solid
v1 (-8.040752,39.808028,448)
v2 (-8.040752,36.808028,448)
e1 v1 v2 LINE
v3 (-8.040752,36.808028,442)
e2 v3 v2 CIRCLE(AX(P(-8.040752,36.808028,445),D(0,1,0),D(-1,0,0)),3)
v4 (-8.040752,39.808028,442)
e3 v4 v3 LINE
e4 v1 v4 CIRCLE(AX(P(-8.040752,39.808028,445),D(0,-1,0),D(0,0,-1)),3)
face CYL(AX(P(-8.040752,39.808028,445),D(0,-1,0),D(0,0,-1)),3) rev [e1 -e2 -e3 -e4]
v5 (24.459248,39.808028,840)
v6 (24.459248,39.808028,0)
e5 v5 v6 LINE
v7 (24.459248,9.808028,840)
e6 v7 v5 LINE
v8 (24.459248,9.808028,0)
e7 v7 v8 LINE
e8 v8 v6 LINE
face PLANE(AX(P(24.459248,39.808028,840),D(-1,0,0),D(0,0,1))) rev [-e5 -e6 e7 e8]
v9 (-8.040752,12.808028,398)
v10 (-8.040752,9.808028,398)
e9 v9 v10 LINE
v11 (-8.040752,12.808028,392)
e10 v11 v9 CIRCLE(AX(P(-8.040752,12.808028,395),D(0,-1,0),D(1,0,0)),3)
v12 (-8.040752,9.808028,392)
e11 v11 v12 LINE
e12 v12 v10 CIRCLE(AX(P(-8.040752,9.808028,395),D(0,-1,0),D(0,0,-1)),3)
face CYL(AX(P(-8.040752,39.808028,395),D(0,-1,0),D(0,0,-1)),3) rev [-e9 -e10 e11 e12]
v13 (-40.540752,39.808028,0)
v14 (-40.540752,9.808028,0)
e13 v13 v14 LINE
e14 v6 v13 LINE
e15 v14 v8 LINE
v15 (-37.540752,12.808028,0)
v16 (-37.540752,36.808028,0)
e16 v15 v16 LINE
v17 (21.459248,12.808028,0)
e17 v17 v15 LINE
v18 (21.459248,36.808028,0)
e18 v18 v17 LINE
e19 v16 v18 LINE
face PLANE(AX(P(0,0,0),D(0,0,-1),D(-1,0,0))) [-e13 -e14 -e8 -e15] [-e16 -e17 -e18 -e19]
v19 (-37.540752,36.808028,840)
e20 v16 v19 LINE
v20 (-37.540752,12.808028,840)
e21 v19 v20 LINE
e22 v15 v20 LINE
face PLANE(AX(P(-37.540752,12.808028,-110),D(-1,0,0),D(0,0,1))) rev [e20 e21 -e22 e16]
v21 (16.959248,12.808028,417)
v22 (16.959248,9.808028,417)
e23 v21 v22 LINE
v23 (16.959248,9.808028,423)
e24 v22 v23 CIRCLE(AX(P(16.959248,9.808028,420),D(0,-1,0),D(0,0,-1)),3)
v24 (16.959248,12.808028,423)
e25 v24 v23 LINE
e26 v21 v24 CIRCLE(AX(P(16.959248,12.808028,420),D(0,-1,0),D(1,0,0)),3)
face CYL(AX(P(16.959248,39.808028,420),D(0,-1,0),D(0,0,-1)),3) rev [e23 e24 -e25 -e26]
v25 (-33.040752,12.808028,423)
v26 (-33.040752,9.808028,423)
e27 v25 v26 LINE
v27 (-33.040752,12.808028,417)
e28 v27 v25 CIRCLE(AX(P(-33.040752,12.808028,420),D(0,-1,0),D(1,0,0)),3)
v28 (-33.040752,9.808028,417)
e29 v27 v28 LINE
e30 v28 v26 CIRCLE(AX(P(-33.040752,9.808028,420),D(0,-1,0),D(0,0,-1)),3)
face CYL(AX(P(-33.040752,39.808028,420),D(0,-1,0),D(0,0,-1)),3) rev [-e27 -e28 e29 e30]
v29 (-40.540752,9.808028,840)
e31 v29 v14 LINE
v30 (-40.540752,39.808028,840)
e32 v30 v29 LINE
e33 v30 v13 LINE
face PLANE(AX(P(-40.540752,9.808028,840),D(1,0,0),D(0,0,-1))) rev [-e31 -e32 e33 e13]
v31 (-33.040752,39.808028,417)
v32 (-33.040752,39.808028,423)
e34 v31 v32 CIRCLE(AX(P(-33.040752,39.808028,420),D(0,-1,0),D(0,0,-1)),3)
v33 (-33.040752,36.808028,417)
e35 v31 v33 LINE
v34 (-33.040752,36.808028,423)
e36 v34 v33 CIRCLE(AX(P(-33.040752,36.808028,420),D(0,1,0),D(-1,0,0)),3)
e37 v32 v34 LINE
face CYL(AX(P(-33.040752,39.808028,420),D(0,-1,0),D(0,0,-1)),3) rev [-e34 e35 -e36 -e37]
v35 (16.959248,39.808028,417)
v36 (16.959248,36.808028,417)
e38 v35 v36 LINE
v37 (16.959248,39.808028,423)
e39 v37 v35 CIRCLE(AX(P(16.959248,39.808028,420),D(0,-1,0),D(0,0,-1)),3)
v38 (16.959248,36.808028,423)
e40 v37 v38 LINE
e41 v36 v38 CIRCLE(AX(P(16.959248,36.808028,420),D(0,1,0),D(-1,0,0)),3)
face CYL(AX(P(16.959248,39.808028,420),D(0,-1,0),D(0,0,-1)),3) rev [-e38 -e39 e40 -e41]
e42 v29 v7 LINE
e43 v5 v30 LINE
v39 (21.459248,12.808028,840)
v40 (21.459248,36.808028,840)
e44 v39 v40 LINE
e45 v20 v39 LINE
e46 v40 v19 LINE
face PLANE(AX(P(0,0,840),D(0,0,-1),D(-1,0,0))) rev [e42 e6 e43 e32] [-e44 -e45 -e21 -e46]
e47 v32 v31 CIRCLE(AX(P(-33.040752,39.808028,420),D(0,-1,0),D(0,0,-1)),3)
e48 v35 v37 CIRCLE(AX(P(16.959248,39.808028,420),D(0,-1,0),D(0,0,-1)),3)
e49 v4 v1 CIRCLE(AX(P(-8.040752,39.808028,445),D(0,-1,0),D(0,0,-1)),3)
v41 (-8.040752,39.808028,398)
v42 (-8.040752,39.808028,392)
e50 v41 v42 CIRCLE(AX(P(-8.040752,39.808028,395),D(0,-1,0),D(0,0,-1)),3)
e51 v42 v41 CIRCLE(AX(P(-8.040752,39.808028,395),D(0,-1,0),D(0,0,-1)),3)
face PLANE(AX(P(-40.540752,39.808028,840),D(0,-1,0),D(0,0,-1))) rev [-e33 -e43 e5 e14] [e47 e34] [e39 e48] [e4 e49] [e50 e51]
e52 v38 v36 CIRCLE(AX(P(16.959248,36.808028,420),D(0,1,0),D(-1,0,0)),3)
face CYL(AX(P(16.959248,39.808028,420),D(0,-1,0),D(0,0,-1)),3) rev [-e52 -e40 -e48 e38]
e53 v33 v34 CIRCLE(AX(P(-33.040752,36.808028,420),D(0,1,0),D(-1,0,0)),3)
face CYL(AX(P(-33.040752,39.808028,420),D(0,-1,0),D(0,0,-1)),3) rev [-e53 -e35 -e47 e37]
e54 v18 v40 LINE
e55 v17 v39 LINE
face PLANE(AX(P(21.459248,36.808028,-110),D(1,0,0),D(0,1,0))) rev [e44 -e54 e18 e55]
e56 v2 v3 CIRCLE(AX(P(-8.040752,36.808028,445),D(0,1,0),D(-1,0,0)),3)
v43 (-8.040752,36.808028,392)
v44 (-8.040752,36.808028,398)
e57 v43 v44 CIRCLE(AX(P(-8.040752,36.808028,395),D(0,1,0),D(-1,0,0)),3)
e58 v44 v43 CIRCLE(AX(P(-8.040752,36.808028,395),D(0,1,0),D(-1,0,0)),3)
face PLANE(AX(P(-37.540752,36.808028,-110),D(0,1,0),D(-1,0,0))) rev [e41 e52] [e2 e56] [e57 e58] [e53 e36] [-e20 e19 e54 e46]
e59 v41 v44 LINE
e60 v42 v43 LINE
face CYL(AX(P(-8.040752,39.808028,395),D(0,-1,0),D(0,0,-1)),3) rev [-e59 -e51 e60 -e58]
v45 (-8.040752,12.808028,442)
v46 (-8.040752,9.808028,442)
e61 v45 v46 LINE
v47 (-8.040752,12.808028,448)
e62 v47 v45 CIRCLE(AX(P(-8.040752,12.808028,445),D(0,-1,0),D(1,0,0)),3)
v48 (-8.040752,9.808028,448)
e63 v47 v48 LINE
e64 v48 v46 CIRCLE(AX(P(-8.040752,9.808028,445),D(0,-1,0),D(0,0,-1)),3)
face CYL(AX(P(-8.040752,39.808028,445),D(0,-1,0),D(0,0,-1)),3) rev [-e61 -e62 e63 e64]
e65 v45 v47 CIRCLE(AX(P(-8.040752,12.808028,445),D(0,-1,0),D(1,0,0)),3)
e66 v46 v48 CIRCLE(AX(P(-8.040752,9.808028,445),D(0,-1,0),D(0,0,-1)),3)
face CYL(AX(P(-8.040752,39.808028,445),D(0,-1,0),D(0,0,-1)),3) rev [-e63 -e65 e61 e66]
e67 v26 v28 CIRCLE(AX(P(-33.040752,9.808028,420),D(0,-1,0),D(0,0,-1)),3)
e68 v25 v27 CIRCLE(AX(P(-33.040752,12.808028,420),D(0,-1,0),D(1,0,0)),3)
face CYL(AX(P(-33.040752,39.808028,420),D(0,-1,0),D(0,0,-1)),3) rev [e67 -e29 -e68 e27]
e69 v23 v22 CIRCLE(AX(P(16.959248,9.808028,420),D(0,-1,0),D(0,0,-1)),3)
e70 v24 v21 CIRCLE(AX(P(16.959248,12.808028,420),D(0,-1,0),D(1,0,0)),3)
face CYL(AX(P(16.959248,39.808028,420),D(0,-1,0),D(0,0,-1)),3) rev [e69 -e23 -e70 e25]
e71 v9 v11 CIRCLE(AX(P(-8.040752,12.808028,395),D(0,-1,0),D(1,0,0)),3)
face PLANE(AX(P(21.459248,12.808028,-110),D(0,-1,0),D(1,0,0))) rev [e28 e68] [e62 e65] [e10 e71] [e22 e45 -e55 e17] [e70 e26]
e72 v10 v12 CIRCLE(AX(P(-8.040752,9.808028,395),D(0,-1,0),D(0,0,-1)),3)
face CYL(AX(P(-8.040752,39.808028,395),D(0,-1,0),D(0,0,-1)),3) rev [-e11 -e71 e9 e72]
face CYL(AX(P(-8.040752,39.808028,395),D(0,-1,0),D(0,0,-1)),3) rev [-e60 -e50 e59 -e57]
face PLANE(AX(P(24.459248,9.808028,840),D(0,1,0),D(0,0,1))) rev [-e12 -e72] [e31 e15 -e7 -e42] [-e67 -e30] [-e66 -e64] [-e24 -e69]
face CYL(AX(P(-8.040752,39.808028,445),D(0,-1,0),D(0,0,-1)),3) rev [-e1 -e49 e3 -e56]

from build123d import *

# Parameters (mm, degrees)
SKETCH1_W           = 65
SKETCH1_H           = 30
BOSS_EXTRUDE1_DEPTH = 840
SKETCH2_W           = 59
SKETCH2_H           = 24
CUT_EXTRUDE1_DEPTH  = 950
SKETCH5_R           = 3
CUT_EXTRUDE3_DEPTH  = 842.512657385


with BuildPart() as part:
    # Sketch1 → Boss-Extrude1 (new body)
    with BuildSketch(Plane.XY):
        with Locations((-8.040751589, 24.808027615)):
            Rectangle(SKETCH1_W, SKETCH1_H)
    extrude(amount=BOSS_EXTRUDE1_DEPTH)

    # Sketch2 → Cut-Extrude1 (cut)
    with BuildSketch(Plane.XY.offset(840)):
        with Locations((-8.040751589, 24.808027615)):
            Rectangle(SKETCH2_W, SKETCH2_H)
    extrude(amount=-CUT_EXTRUDE1_DEPTH, mode=Mode.SUBTRACT)

    # Sketch5 → Cut-Extrude3 (cut, through all)
    with BuildSketch(Plane(origin=(0, 9.808027615, 0), x_dir=(-1, 0, 0), z_dir=(0, -1, 0))):
        with Locations(Location((8.040751589, -395, 0), (0, 0, 90))):
            Circle(SKETCH5_R)
        with Locations(Location((33.040751589, -420, 0), (0, 0, 90))):
            Circle(SKETCH5_R)
        with Locations(Location((8.040751589, -445, 0), (0, 0, 90))):
            Circle(SKETCH5_R)
        with Locations(Location((-16.959248411, -420, 0), (0, 0, 90))):
            Circle(SKETCH5_R)
    extrude(amount=-CUT_EXTRUDE3_DEPTH, mode=Mode.SUBTRACT)


solid = part.part
